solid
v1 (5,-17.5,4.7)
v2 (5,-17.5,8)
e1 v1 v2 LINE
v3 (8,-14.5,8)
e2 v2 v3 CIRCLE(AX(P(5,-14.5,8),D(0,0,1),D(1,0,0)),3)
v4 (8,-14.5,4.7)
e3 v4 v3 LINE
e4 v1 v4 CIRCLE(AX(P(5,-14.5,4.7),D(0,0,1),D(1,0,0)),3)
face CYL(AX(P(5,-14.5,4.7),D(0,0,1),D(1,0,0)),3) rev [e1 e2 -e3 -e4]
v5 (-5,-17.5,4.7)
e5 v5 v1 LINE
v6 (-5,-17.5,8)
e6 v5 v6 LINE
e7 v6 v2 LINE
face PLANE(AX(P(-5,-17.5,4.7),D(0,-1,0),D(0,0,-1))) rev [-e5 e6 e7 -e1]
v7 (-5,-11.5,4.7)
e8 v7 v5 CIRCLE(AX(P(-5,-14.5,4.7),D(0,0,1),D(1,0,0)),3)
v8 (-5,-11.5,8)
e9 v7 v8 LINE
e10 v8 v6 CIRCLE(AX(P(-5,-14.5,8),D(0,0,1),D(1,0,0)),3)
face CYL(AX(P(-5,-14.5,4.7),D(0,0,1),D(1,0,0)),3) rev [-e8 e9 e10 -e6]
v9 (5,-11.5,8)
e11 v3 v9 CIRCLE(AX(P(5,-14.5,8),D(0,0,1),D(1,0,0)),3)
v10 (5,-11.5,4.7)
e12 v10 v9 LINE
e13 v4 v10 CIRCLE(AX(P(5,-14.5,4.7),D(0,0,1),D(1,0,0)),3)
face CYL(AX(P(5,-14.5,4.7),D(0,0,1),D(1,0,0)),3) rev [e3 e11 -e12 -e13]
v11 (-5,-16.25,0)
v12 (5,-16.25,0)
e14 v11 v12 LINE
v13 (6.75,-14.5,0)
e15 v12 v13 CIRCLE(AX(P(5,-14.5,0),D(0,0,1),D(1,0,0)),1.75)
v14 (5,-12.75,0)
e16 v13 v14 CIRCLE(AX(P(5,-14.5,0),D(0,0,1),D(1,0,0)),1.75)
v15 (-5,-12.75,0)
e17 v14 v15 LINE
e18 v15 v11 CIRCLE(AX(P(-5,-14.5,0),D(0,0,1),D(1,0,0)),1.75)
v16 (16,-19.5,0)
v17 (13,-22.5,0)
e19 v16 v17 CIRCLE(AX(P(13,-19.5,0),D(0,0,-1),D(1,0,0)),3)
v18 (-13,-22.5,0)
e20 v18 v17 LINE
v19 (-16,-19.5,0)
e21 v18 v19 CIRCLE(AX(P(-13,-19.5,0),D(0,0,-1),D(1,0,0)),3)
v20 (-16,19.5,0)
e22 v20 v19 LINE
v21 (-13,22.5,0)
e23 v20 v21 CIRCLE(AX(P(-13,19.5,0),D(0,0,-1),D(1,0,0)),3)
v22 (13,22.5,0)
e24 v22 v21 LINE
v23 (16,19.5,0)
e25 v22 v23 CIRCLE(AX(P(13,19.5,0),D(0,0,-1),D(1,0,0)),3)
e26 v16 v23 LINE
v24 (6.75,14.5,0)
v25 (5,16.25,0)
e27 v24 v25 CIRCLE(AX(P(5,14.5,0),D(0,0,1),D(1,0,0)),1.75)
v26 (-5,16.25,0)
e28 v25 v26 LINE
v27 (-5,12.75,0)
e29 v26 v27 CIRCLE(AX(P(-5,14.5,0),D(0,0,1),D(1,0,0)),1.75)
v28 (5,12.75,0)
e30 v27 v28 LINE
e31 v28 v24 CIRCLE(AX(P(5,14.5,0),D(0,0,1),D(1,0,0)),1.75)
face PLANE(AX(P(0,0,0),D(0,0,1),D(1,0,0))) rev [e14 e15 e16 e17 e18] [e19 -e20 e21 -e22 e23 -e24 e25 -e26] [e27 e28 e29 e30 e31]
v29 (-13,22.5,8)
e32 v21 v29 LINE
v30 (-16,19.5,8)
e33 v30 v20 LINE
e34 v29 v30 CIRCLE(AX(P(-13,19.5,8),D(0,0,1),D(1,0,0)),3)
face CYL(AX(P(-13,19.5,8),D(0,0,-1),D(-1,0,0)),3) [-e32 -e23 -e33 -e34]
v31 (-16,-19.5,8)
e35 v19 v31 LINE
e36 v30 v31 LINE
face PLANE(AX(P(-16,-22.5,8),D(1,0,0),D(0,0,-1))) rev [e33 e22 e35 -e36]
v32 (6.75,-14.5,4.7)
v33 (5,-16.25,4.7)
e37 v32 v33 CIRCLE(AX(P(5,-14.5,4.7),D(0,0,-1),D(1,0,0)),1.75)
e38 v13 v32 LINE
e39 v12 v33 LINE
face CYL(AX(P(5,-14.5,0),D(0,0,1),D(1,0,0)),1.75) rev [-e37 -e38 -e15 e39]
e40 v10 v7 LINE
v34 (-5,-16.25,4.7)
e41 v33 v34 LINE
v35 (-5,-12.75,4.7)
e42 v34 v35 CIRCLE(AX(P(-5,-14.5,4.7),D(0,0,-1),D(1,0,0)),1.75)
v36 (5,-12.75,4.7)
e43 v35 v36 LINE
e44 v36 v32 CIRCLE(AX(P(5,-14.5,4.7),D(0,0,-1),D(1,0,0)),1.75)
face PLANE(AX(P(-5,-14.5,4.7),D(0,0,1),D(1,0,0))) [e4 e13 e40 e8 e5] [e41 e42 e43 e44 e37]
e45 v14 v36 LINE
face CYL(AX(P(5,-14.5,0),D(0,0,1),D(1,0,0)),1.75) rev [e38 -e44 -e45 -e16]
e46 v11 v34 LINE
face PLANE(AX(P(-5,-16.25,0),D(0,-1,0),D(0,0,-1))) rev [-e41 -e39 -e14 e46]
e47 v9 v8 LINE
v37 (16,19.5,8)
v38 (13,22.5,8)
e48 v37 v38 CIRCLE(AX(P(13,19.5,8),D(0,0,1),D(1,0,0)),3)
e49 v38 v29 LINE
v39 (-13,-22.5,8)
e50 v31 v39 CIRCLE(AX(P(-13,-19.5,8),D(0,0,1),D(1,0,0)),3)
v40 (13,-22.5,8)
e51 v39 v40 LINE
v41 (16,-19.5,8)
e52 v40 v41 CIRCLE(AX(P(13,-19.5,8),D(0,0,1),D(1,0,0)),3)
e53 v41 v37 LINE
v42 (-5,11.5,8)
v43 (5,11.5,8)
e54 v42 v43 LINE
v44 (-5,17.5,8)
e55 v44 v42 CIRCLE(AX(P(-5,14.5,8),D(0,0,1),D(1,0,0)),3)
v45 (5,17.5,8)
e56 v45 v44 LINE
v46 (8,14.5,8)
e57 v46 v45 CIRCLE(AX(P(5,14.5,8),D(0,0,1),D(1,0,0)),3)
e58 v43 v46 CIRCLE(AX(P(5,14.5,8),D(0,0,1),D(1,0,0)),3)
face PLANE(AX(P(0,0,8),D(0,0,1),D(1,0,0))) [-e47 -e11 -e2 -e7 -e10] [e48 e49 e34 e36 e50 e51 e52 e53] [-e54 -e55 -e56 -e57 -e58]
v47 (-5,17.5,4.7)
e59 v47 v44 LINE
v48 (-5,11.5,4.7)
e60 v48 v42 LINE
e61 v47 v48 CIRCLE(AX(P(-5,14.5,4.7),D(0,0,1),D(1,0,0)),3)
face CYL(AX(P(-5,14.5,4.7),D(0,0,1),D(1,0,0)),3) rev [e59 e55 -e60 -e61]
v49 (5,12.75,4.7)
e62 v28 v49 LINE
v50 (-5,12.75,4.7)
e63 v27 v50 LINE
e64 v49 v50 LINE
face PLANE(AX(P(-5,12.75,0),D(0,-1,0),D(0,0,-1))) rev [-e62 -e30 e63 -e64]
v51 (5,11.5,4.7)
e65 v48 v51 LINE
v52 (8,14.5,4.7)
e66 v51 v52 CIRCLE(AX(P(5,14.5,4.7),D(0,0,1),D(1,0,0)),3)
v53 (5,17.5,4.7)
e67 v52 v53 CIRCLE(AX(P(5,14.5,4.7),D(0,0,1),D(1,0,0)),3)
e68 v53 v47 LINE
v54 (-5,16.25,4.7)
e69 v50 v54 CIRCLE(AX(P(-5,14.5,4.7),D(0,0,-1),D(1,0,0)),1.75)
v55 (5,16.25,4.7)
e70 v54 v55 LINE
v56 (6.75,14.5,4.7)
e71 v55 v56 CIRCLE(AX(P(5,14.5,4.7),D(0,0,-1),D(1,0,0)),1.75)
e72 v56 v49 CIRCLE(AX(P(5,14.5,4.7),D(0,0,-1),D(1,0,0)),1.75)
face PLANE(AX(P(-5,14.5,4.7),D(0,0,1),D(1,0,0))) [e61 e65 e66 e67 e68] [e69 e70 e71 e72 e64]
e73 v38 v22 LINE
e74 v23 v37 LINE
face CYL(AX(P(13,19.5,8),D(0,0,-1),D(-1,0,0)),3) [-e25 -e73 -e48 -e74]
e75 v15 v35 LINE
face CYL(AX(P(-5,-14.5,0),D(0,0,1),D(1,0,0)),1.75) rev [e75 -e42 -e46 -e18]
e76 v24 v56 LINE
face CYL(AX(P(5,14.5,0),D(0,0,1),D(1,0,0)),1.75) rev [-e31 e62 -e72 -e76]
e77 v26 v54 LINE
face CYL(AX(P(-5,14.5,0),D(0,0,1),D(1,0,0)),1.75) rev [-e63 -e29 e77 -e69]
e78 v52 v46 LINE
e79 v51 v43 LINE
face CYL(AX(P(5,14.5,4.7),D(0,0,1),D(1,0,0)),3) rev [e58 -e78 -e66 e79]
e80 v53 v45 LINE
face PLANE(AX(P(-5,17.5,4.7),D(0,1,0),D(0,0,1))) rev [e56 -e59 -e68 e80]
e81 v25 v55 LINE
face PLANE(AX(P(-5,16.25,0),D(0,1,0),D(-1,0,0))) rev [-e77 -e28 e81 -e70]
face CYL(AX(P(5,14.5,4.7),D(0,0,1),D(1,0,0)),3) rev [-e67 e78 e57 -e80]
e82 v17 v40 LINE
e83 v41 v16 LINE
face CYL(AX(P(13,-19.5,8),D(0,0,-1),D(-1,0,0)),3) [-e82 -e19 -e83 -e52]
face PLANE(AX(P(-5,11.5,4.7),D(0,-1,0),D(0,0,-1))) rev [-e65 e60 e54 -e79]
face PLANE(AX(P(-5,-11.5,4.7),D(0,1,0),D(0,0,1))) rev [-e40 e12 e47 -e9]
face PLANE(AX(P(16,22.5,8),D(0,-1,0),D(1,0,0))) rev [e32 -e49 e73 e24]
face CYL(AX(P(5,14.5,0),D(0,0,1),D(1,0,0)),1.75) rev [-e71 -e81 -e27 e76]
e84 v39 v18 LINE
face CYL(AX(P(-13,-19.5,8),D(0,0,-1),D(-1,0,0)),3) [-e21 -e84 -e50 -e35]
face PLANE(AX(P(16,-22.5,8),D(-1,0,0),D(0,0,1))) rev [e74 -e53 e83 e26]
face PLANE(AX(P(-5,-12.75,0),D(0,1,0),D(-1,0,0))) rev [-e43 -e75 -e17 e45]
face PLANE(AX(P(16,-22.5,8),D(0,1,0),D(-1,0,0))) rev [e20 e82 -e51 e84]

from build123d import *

# Parameters (mm, degrees)
SKETCH1_W           = 32
SKETCH1_H           = 45
BOSS_EXTRUDE1_DEPTH = 8
FILLET1_R           = 3
CUT_EXTRUDE1_DEPTH  = 29.744564704
CUT_EXTRUDE2_DEPTH  = 3.3


with BuildPart() as part:
    # Sketch1 → Boss-Extrude1 (new body)
    with BuildSketch(Plane.XY):
        Rectangle(SKETCH1_W, SKETCH1_H)
    extrude(amount=BOSS_EXTRUDE1_DEPTH)

    # Fillet1
    fillet1_edges = [part.edges().sort_by_distance(p)[0] for p in [
        (-16, 22.5, 4),
        (16, 22.5, 4),
        (16, -22.5, 4),
        (-16, -22.5, 4),
    ]]
    fillet(fillet1_edges, radius=FILLET1_R)

    # Sketch2 → Cut-Extrude1 (cut, through all)
    with BuildSketch(Plane.XY.offset(8)):
        with BuildLine():
            Line((-5, 16.25), (5, 16.25))
            ThreePointArc((5, 16.25), (6.75, 14.5), (5, 12.75))
            Line((5, 12.75), (-5, 12.75))
            ThreePointArc((-5, 12.75), (-6.75, 14.5), (-5, 16.25))
        make_face()
        with BuildLine():
            Line((-5, -12.75), (5, -12.75))
            ThreePointArc((5, -12.75), (6.75, -14.5), (5, -16.25))
            Line((5, -16.25), (-5, -16.25))
            ThreePointArc((-5, -16.25), (-6.75, -14.5), (-5, -12.75))
        make_face()
    extrude(amount=-CUT_EXTRUDE1_DEPTH, mode=Mode.SUBTRACT)

    # Sketch3 → Cut-Extrude2 (cut)
    with BuildSketch(Plane.XY.offset(8)):
        with BuildLine():
            Line((-5, 17.5), (5, 17.5))
            ThreePointArc((5, 17.5), (8, 14.5), (5, 11.5))
            Line((5, 11.5), (-5, 11.5))
            ThreePointArc((-5, 11.5), (-8, 14.5), (-5, 17.5))
        make_face()
        with BuildLine():
            Line((-5, -11.5), (5, -11.5))
            ThreePointArc((5, -11.5), (8, -14.5), (5, -17.5))
            Line((5, -17.5), (-5, -17.5))
            ThreePointArc((-5, -17.5), (-8, -14.5), (-5, -11.5))
        make_face()
    extrude(amount=-CUT_EXTRUDE2_DEPTH, mode=Mode.SUBTRACT)


solid = part.part
